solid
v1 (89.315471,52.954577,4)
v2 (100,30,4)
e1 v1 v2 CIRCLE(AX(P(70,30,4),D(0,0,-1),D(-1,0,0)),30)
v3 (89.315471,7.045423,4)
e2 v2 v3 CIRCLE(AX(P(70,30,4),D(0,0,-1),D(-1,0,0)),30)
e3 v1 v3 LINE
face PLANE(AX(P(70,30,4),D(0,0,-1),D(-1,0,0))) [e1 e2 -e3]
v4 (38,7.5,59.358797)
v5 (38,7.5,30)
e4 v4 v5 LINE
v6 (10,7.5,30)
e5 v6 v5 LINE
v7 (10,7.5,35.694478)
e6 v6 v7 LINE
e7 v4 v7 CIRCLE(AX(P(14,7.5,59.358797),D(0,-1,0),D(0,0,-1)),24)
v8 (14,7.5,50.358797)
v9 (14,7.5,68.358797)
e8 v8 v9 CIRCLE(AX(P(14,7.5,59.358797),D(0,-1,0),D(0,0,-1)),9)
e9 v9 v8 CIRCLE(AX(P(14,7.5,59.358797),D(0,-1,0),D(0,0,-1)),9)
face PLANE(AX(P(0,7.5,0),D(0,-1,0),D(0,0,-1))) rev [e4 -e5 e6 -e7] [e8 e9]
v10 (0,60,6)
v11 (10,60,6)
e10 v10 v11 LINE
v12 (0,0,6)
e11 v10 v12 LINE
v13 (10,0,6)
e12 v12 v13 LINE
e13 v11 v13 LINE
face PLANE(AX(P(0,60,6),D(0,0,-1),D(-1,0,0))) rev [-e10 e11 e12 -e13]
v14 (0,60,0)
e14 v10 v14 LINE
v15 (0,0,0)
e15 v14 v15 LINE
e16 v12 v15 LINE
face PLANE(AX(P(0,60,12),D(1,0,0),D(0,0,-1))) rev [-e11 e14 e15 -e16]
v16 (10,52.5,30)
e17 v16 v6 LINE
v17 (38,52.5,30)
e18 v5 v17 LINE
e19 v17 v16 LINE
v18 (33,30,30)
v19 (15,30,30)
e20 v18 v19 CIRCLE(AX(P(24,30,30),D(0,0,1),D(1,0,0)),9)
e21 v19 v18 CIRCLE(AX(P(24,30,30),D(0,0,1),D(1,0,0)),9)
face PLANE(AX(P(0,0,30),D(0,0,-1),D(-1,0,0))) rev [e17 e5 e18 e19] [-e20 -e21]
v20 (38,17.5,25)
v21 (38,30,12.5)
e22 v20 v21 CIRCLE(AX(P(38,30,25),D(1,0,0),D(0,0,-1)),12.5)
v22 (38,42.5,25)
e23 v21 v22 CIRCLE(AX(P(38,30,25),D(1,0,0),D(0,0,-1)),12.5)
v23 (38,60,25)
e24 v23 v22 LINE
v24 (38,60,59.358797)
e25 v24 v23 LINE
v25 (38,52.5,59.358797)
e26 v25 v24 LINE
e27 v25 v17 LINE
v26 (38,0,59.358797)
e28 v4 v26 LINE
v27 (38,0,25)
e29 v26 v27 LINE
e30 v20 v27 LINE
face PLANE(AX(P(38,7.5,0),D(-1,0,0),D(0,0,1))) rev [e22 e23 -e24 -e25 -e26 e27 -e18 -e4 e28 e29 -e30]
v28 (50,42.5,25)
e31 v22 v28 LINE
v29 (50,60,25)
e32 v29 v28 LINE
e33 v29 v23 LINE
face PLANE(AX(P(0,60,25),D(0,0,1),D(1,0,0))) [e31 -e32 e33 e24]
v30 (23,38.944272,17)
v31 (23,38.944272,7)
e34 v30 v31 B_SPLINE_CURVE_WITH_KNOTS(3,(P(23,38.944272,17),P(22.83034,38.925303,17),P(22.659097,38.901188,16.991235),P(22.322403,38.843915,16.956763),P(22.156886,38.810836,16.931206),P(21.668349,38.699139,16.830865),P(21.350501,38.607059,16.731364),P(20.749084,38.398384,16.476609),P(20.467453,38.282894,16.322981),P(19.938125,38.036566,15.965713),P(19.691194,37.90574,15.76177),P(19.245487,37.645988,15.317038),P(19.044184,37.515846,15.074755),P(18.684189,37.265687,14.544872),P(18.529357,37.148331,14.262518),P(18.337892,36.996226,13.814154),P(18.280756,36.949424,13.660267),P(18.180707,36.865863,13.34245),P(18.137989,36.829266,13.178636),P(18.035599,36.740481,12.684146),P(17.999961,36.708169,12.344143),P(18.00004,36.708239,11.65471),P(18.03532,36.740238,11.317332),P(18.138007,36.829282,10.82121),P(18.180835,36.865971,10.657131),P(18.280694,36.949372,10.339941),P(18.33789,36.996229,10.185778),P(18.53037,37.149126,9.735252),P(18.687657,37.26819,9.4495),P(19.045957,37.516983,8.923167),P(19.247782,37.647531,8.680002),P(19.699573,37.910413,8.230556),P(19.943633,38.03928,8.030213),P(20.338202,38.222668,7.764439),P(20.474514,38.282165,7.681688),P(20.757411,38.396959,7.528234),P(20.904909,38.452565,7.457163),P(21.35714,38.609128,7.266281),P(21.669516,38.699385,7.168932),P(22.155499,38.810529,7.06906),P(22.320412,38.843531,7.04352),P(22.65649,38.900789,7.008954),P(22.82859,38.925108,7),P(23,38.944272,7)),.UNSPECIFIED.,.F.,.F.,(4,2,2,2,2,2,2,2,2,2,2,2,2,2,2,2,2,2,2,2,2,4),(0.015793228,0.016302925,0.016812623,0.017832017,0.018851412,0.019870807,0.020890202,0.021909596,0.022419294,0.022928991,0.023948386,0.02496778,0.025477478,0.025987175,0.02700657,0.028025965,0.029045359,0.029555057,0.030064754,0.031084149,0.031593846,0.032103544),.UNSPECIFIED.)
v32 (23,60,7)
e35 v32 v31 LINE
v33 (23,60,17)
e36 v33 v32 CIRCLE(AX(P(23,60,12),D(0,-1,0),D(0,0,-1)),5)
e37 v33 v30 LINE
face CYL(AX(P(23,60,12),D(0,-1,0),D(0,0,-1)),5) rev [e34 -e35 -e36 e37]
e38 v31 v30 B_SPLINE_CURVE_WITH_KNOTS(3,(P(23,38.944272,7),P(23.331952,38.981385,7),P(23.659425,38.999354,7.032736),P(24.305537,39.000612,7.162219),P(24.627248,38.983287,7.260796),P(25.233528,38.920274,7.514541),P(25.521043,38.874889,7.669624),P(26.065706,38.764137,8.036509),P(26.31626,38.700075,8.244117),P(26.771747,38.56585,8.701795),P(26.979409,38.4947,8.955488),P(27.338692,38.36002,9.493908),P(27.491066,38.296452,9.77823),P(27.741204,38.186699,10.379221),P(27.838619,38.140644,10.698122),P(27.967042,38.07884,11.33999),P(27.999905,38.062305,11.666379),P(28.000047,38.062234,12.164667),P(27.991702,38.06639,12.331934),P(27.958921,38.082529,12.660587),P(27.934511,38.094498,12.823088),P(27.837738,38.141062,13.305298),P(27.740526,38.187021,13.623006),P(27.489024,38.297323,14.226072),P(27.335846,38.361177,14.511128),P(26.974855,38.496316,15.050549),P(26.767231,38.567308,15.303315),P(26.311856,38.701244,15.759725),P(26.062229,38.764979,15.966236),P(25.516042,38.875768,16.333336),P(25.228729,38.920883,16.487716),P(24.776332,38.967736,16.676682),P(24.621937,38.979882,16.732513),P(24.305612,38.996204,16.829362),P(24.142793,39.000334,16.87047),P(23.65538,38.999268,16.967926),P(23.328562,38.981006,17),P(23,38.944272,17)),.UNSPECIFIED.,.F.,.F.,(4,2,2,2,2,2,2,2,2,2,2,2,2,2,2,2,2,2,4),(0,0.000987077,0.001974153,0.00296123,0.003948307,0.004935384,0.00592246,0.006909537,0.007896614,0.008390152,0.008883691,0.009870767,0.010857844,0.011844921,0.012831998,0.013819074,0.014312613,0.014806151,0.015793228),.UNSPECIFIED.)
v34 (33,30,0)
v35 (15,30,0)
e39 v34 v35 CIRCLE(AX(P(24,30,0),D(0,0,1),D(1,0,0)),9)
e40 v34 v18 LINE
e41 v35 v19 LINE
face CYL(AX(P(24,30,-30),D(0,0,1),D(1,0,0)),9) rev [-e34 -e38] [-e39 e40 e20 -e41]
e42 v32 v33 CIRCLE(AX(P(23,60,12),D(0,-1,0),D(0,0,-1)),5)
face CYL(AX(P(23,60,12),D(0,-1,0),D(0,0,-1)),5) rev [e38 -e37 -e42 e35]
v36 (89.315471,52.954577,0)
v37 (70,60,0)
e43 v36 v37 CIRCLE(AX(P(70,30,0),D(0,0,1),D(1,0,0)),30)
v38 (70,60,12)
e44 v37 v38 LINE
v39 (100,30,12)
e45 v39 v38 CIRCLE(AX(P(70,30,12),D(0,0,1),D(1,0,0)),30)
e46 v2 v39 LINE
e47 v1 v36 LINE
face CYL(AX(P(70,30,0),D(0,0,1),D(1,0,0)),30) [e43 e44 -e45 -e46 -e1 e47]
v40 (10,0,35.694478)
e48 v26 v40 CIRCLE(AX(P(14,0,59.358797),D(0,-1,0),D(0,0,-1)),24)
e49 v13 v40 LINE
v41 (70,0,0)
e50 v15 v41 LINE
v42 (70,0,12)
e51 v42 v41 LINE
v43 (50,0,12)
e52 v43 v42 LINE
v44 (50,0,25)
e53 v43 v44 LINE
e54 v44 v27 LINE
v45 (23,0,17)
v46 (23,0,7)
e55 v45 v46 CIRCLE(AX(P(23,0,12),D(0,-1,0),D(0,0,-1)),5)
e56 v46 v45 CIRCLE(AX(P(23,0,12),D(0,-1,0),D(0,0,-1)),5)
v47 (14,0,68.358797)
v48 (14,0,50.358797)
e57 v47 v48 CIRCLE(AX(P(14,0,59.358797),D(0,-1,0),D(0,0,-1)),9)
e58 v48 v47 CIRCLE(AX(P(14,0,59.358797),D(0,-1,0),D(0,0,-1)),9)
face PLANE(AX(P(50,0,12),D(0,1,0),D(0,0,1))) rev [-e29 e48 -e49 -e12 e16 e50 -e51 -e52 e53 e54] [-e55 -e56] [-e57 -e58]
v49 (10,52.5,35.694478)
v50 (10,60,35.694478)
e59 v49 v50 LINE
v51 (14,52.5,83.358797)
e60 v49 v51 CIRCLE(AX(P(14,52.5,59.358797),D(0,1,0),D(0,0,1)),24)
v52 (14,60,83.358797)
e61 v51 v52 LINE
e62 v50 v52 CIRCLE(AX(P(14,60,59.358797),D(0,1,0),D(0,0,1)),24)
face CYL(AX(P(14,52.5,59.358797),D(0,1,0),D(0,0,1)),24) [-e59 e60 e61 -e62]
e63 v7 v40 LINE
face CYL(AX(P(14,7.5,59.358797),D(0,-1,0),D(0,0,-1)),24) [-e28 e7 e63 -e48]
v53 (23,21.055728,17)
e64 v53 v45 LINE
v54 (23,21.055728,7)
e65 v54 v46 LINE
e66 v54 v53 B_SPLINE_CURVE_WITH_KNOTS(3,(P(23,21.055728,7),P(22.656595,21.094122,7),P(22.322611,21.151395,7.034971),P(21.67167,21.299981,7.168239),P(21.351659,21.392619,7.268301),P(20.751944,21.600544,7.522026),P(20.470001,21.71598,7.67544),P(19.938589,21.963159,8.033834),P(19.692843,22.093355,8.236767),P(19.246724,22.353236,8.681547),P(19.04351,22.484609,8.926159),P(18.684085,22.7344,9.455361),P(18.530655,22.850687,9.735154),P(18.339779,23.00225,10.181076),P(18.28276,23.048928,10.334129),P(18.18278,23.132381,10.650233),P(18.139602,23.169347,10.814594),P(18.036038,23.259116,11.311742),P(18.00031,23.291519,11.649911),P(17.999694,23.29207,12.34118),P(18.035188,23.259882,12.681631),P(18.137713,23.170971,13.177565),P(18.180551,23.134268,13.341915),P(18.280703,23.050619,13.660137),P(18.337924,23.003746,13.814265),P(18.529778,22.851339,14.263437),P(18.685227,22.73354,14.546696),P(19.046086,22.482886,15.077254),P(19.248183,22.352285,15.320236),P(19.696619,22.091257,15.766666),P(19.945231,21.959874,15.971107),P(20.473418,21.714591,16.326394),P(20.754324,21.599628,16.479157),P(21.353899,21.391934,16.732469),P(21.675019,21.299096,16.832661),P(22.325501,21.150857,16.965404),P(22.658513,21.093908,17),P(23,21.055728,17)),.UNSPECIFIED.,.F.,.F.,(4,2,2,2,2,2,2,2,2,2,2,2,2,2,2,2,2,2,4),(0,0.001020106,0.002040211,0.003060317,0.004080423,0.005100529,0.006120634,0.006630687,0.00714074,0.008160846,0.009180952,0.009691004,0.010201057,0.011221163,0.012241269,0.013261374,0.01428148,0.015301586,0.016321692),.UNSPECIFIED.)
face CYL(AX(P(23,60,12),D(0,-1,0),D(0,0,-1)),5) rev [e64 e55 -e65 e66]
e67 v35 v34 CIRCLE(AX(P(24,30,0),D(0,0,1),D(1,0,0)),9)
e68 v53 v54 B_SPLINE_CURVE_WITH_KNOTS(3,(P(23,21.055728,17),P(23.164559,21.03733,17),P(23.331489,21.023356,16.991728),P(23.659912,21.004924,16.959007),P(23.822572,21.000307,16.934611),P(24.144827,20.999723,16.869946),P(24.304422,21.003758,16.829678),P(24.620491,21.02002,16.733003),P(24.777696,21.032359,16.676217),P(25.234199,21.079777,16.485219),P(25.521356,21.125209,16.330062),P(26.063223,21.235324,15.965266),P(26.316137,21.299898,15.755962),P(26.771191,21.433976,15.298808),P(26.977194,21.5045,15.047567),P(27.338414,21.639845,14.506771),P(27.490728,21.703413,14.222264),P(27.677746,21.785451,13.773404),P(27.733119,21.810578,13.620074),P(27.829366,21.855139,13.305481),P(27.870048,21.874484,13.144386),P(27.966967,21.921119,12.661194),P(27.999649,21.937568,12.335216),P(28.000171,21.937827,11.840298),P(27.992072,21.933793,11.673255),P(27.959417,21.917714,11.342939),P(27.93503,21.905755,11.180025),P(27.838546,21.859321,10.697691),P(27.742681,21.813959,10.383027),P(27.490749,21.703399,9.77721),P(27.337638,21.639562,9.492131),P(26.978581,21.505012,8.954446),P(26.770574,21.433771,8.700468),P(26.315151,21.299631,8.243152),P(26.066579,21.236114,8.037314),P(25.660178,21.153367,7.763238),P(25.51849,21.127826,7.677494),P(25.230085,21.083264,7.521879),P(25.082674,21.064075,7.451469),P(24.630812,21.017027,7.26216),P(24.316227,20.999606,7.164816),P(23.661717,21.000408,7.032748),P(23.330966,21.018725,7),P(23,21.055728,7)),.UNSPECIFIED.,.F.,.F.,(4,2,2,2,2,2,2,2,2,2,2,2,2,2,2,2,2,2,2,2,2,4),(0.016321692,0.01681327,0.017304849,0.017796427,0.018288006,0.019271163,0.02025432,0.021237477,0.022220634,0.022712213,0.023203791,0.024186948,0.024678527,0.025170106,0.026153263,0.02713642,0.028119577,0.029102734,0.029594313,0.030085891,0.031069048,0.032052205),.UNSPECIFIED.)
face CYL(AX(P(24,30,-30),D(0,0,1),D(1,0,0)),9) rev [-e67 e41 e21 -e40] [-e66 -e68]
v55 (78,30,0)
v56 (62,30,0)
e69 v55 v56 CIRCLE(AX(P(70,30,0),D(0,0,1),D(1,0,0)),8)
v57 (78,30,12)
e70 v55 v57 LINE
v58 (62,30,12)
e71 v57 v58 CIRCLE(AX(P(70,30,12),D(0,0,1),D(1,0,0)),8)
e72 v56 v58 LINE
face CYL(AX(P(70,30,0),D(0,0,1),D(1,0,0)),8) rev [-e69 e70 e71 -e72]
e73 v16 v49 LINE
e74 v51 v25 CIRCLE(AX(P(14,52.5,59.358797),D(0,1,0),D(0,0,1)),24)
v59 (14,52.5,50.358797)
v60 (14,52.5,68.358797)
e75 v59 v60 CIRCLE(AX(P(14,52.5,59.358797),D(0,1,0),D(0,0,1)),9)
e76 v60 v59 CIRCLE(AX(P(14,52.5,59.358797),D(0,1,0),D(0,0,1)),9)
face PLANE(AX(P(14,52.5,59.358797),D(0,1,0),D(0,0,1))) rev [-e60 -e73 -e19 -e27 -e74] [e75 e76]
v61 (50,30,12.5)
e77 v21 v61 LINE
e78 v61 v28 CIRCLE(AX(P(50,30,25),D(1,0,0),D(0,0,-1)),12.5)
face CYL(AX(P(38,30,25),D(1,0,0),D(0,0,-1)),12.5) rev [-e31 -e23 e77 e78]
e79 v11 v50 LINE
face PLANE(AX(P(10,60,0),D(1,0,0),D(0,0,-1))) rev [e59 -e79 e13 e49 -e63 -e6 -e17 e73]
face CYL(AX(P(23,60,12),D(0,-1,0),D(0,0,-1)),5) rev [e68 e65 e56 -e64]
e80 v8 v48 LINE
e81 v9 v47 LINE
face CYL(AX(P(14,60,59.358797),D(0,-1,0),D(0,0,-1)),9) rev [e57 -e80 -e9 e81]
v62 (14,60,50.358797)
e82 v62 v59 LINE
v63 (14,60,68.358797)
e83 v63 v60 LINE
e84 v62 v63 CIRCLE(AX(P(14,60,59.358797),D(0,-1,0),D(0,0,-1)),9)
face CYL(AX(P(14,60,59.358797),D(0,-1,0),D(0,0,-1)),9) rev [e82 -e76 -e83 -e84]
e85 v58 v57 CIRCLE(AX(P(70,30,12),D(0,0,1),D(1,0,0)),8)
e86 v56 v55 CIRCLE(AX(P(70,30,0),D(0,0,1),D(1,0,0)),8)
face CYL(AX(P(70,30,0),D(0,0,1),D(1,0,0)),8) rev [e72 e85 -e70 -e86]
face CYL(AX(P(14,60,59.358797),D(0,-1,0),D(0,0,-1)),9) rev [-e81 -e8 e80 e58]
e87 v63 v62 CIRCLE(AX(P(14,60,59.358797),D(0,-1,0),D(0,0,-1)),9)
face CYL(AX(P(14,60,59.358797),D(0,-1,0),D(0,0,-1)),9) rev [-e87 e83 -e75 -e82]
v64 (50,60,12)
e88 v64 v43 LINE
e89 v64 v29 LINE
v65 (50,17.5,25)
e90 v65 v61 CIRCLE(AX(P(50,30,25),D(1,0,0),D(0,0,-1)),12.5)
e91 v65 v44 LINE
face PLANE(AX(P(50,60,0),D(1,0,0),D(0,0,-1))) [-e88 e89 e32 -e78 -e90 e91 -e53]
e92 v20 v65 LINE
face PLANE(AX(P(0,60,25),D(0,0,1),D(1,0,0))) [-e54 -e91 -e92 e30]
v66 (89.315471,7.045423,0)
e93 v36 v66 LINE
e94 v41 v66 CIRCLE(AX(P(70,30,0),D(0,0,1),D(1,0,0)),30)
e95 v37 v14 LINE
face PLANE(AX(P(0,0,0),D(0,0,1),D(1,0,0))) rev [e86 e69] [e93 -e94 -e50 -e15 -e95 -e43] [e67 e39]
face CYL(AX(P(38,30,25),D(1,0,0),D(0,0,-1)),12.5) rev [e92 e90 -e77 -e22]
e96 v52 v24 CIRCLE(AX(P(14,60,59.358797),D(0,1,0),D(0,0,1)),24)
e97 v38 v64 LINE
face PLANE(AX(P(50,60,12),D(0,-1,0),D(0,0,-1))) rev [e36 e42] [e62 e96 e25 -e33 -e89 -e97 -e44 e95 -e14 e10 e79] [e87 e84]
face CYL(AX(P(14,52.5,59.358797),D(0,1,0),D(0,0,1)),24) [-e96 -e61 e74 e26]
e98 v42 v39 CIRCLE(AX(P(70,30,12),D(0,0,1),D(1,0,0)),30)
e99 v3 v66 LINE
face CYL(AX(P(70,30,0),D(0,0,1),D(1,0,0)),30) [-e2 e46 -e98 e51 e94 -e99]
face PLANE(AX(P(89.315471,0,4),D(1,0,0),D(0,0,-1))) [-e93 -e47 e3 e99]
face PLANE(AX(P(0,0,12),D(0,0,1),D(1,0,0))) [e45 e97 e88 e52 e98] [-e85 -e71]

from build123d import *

# Parameters (mm, degrees)
BASE_PLATE_DEPTH           = 12
BASE_PROFILE_CUT_SKETCH_W  = 10
BASE_PROFILE_CUT_SKETCH_H  = 6
BASE_PROFILE_CUT_DEPTH     = 60
SIDE_NOTCH_SKETCH_W        = 13
SIDE_NOTCH_SKETCH_H        = 12
SIDE_NOTCH_CUT_DEPTH       = 60
UPRIGHT_WEB_SKETCH_W       = 12
UPRIGHT_WEB_SKETCH_H       = 60
UPRIGHT_WEB_DEPTH          = 12
LUG_BLOCK_SKETCH_W         = 12
LUG_BLOCK_SKETCH_H         = 13
LUG_BLOCK_DEPTH            = 60
WEB_PAD_SKETCH_W           = 12
WEB_PAD_SKETCH_H           = 60
WEB_PAD_1MM_DEPTH          = 1
EAR_BASE_DEPTH             = 12
UPPER_CLEVIS_LUG_DEPTH     = 7.5
LOWER_START                = -7.5
LOWER_CLEVIS_LUG_DEPTH     = 7.5
CLEVIS_SPACER_SKETCH_W     = 13
CLEVIS_SPACER_SKETCH_H     = 45
CLEVIS_SPACER_BLOCK_DEPTH  = 28
LUG_PAD_SKETCH_W           = 28
LUG_PAD_SKETCH_H           = 45
LUG_PAD_5MM_DEPTH          = 5
CLEVIS_SLOT_CUT_DEPTH      = 12
HOLE_10_SKETCH_R           = 5
HOLE_10_DEPTH              = 60
UPPER_PIN_HOLE_18_SKETCH_R = 9
UPPER_PIN_HOLE_18_DEPTH    = 60
LOWER_PIN_HOLE_18_SKETCH_R = 9
LOWER_PIN_HOLE_18_DEPTH    = 60
EAR_ROUND_CUT_DEPTH        = 60
EAR_BOSS_SKETCH_W          = 12
EAR_BOSS_SKETCH_H          = 60
EAR_BOSS_7MM_DEPTH         = 7
EAR_PLATE_DEPTH            = 12
EAR_BORE_16_SKETCH_R       = 8
EAR_BORE_16_DEPTH          = 12
EAR_START                  = -4
EAR_RELIEF_CUT_A_DEPTH     = 4
EAR_RELIEF_CUT_B_DEPTH     = 4


with BuildPart() as part:
    # Base Plate Sketch → Base Plate (new body)
    with BuildSketch(Plane.XY):
        Polygon((0, 0), (50, 0), (63, 0), (63, 60), (50, 60), (0, 60), align=None)
    extrude(amount=BASE_PLATE_DEPTH)

    # Base Profile Cut Sketch → Base Profile Cut (cut)
    with BuildSketch(Plane.XZ):
        with Locations((5, 9)):
            Rectangle(BASE_PROFILE_CUT_SKETCH_W, BASE_PROFILE_CUT_SKETCH_H)
    extrude(amount=-BASE_PROFILE_CUT_DEPTH, mode=Mode.SUBTRACT)

    # Side Notch Sketch → Side Notch Cut (cut)
    with BuildSketch(Plane.XZ):
        with Locations((56.5, 6)):
            Rectangle(SIDE_NOTCH_SKETCH_W, SIDE_NOTCH_SKETCH_H)
    extrude(amount=-SIDE_NOTCH_CUT_DEPTH, mode=Mode.SUBTRACT)

    # Upright Web Sketch → Upright Web (add)
    with BuildSketch(Plane.XY.offset(12)):
        with Locations((56, 30)):
            Rectangle(UPRIGHT_WEB_SKETCH_W, UPRIGHT_WEB_SKETCH_H)
    extrude(amount=-UPRIGHT_WEB_DEPTH)

    # Lug Block Sketch → Lug Block (add)
    with BuildSketch(Plane.XZ):
        with Locations((44, 18.5)):
            Rectangle(LUG_BLOCK_SKETCH_W, LUG_BLOCK_SKETCH_H)
    extrude(amount=-LUG_BLOCK_DEPTH)

    # Web Pad Sketch → Web Pad 1mm (add)
    with BuildSketch(Plane(origin=(62, 0, 0), x_dir=(0, 0, -1), z_dir=(1, 0, 0))):
        with Locations((-6, 30)):
            Rectangle(WEB_PAD_SKETCH_W, WEB_PAD_SKETCH_H)
    extrude(amount=WEB_PAD_1MM_DEPTH)

    # Ear Base Sketch → Ear Base (add)
    with BuildSketch(Plane.XY.offset(12)):
        with BuildLine():
            Line((63, 60), (63, 0))
            ThreePointArc((63, 0), (93, 30), (63, 60))
        make_face()
    extrude(amount=-EAR_BASE_DEPTH)

    # Upper Clevis Lug Sketch → Upper Clevis Lug (add)
    with BuildSketch(Plane.XZ):
        with BuildLine():
            Line((38, 59.358797437), (38, 25))
            Line((38, 25), (38, 12))
            Line((38, 12), (10, 12))
            Line((10, 12), (10, 35.694478304))
            ThreePointArc((10, 35.694478304), (-1.491933385, 77.689100216), (38, 59.358797437))
        make_face()
    extrude(amount=-UPPER_CLEVIS_LUG_DEPTH)

    # Lower Clevis Lug Sketch → Lower Clevis Lug (add)
    with BuildSketch(Plane(origin=(0, 60, 0), x_dir=(1, 0, 0), z_dir=(0, 1, 0)).offset(LOWER_START)):
        with BuildLine():
            Line((38, -12), (38, -59.358797437))
            ThreePointArc((38, -59.358797437), (-1.491933385, -77.689100216), (10, -35.694478304))
            Line((10, -35.694478304), (10, -12))
            Line((10, -12), (38, -12))
        make_face()
    extrude(amount=LOWER_CLEVIS_LUG_DEPTH)

    # Clevis Spacer Sketch → Clevis Spacer Block (add)
    with BuildSketch(Plane.ZY.offset(-38)):
        with Locations((18.5, 30)):
            Rectangle(CLEVIS_SPACER_SKETCH_W, CLEVIS_SPACER_SKETCH_H)
    extrude(amount=CLEVIS_SPACER_BLOCK_DEPTH)

    # Lug Pad Sketch → Lug Pad 5mm (add)
    with BuildSketch(Plane.XY.offset(25)):
        with Locations((24, 30)):
            Rectangle(LUG_PAD_SKETCH_W, LUG_PAD_SKETCH_H)
    extrude(amount=LUG_PAD_5MM_DEPTH)

    # Clevis Slot Sketch → Clevis Slot Cut (cut)
    with BuildSketch(Plane(origin=(50, 0, 0), x_dir=(0, 0, -1), z_dir=(1, 0, 0))):
        with BuildLine():
            Line((-25, 42.5), (-25, 17.5))
            ThreePointArc((-25, 17.5), (-12.5, 30), (-25, 42.5))
        make_face()
    extrude(amount=-CLEVIS_SLOT_CUT_DEPTH, mode=Mode.SUBTRACT)

    # Hole Ø10 Sketch → Hole Ø10 (cut)
    with BuildSketch(Plane.XZ):
        with Locations(Location((23, 12, 0), (0, 0, 270))):
            Circle(HOLE_10_SKETCH_R)
    extrude(amount=-HOLE_10_DEPTH, mode=Mode.SUBTRACT)

    # Upper Pin Hole Ø18 Sketch → Upper Pin Hole Ø18 (cut)
    with BuildSketch(Plane.XZ):
        with Locations(Location((14, 59.358797437, 0), (0, 0, 270))):
            Circle(UPPER_PIN_HOLE_18_SKETCH_R)
    extrude(amount=-UPPER_PIN_HOLE_18_DEPTH, mode=Mode.SUBTRACT)

    # Lower Pin Hole Ø18 Sketch → Lower Pin Hole Ø18 (cut)
    with BuildSketch(Plane.XY.offset(30)):
        with Locations((24, 30)):
            Circle(LOWER_PIN_HOLE_18_SKETCH_R)
    extrude(amount=-LOWER_PIN_HOLE_18_DEPTH, mode=Mode.SUBTRACT)

    # Ear Round Cut Sketch → Ear Round Cut (cut)
    with BuildSketch(Plane.XY.offset(12)):
        with BuildLine():
            Line((63, 60), (63, 0))
            ThreePointArc((63, 0), (93, 30), (63, 60))
        make_face()
    extrude(amount=-EAR_ROUND_CUT_DEPTH, mode=Mode.SUBTRACT)

    # Ear Boss Sketch → Ear Boss 7mm (add)
    with BuildSketch(Plane(origin=(63, 0, 0), x_dir=(0, 0, -1), z_dir=(1, 0, 0))):
        with Locations((-6, 30)):
            Rectangle(EAR_BOSS_SKETCH_W, EAR_BOSS_SKETCH_H)
    extrude(amount=EAR_BOSS_7MM_DEPTH)

    # Ear Plate Sketch → Ear Plate (add)
    with BuildSketch(Plane.XY.offset(12)):
        with BuildLine():
            Line((70, 60), (70, 0))
            ThreePointArc((70, 0), (100, 30), (70, 60))
        make_face()
    extrude(amount=-EAR_PLATE_DEPTH)

    # Ear Bore Ø16 Sketch → Ear Bore Ø16 (cut)
    with BuildSketch(Plane.XY.offset(12)):
        with Locations((70, 30)):
            Circle(EAR_BORE_16_SKETCH_R)
    extrude(amount=-EAR_BORE_16_DEPTH, mode=Mode.SUBTRACT)

    # Ear Relief A Sketch → Ear Relief Cut A (cut)
    with BuildSketch(Plane(origin=(0, 0, 0), x_dir=(-1, 0, 0), z_dir=(0, 0, -1)).offset(EAR_START)):
        with BuildLine():
            Line((-93.315470525, 48.878263537), (-93.315470525, 11.121736463))
            ThreePointArc((-93.315470525, 11.121736463), (-100, 30), (-93.315470525, 48.878263537))
        make_face()
    extrude(amount=EAR_RELIEF_CUT_A_DEPTH, mode=Mode.SUBTRACT)

    # Ear Relief B Sketch → Ear Relief Cut B (cut)
    with BuildSketch(Plane(origin=(0, 0, 0), x_dir=(-1, 0, 0), z_dir=(0, 0, -1)).offset(EAR_START)):
        with BuildLine():
            Line((-89.315470525, 7.045423149), (-89.315470525, 30))
            Line((-89.315470525, 30), (-89.315470525, 52.954576851))
            ThreePointArc((-89.315470525, 52.954576851), (-91.41269171, 51.011821285), (-93.315470525, 48.878263537))
            Line((-93.315470525, 48.878263537), (-93.315470525, 11.121736463))
            ThreePointArc((-93.315470525, 11.121736463), (-91.41269171, 8.988178715), (-89.315470525, 7.045423149))
        make_face()
    extrude(amount=EAR_RELIEF_CUT_B_DEPTH, mode=Mode.SUBTRACT)


solid = part.part
